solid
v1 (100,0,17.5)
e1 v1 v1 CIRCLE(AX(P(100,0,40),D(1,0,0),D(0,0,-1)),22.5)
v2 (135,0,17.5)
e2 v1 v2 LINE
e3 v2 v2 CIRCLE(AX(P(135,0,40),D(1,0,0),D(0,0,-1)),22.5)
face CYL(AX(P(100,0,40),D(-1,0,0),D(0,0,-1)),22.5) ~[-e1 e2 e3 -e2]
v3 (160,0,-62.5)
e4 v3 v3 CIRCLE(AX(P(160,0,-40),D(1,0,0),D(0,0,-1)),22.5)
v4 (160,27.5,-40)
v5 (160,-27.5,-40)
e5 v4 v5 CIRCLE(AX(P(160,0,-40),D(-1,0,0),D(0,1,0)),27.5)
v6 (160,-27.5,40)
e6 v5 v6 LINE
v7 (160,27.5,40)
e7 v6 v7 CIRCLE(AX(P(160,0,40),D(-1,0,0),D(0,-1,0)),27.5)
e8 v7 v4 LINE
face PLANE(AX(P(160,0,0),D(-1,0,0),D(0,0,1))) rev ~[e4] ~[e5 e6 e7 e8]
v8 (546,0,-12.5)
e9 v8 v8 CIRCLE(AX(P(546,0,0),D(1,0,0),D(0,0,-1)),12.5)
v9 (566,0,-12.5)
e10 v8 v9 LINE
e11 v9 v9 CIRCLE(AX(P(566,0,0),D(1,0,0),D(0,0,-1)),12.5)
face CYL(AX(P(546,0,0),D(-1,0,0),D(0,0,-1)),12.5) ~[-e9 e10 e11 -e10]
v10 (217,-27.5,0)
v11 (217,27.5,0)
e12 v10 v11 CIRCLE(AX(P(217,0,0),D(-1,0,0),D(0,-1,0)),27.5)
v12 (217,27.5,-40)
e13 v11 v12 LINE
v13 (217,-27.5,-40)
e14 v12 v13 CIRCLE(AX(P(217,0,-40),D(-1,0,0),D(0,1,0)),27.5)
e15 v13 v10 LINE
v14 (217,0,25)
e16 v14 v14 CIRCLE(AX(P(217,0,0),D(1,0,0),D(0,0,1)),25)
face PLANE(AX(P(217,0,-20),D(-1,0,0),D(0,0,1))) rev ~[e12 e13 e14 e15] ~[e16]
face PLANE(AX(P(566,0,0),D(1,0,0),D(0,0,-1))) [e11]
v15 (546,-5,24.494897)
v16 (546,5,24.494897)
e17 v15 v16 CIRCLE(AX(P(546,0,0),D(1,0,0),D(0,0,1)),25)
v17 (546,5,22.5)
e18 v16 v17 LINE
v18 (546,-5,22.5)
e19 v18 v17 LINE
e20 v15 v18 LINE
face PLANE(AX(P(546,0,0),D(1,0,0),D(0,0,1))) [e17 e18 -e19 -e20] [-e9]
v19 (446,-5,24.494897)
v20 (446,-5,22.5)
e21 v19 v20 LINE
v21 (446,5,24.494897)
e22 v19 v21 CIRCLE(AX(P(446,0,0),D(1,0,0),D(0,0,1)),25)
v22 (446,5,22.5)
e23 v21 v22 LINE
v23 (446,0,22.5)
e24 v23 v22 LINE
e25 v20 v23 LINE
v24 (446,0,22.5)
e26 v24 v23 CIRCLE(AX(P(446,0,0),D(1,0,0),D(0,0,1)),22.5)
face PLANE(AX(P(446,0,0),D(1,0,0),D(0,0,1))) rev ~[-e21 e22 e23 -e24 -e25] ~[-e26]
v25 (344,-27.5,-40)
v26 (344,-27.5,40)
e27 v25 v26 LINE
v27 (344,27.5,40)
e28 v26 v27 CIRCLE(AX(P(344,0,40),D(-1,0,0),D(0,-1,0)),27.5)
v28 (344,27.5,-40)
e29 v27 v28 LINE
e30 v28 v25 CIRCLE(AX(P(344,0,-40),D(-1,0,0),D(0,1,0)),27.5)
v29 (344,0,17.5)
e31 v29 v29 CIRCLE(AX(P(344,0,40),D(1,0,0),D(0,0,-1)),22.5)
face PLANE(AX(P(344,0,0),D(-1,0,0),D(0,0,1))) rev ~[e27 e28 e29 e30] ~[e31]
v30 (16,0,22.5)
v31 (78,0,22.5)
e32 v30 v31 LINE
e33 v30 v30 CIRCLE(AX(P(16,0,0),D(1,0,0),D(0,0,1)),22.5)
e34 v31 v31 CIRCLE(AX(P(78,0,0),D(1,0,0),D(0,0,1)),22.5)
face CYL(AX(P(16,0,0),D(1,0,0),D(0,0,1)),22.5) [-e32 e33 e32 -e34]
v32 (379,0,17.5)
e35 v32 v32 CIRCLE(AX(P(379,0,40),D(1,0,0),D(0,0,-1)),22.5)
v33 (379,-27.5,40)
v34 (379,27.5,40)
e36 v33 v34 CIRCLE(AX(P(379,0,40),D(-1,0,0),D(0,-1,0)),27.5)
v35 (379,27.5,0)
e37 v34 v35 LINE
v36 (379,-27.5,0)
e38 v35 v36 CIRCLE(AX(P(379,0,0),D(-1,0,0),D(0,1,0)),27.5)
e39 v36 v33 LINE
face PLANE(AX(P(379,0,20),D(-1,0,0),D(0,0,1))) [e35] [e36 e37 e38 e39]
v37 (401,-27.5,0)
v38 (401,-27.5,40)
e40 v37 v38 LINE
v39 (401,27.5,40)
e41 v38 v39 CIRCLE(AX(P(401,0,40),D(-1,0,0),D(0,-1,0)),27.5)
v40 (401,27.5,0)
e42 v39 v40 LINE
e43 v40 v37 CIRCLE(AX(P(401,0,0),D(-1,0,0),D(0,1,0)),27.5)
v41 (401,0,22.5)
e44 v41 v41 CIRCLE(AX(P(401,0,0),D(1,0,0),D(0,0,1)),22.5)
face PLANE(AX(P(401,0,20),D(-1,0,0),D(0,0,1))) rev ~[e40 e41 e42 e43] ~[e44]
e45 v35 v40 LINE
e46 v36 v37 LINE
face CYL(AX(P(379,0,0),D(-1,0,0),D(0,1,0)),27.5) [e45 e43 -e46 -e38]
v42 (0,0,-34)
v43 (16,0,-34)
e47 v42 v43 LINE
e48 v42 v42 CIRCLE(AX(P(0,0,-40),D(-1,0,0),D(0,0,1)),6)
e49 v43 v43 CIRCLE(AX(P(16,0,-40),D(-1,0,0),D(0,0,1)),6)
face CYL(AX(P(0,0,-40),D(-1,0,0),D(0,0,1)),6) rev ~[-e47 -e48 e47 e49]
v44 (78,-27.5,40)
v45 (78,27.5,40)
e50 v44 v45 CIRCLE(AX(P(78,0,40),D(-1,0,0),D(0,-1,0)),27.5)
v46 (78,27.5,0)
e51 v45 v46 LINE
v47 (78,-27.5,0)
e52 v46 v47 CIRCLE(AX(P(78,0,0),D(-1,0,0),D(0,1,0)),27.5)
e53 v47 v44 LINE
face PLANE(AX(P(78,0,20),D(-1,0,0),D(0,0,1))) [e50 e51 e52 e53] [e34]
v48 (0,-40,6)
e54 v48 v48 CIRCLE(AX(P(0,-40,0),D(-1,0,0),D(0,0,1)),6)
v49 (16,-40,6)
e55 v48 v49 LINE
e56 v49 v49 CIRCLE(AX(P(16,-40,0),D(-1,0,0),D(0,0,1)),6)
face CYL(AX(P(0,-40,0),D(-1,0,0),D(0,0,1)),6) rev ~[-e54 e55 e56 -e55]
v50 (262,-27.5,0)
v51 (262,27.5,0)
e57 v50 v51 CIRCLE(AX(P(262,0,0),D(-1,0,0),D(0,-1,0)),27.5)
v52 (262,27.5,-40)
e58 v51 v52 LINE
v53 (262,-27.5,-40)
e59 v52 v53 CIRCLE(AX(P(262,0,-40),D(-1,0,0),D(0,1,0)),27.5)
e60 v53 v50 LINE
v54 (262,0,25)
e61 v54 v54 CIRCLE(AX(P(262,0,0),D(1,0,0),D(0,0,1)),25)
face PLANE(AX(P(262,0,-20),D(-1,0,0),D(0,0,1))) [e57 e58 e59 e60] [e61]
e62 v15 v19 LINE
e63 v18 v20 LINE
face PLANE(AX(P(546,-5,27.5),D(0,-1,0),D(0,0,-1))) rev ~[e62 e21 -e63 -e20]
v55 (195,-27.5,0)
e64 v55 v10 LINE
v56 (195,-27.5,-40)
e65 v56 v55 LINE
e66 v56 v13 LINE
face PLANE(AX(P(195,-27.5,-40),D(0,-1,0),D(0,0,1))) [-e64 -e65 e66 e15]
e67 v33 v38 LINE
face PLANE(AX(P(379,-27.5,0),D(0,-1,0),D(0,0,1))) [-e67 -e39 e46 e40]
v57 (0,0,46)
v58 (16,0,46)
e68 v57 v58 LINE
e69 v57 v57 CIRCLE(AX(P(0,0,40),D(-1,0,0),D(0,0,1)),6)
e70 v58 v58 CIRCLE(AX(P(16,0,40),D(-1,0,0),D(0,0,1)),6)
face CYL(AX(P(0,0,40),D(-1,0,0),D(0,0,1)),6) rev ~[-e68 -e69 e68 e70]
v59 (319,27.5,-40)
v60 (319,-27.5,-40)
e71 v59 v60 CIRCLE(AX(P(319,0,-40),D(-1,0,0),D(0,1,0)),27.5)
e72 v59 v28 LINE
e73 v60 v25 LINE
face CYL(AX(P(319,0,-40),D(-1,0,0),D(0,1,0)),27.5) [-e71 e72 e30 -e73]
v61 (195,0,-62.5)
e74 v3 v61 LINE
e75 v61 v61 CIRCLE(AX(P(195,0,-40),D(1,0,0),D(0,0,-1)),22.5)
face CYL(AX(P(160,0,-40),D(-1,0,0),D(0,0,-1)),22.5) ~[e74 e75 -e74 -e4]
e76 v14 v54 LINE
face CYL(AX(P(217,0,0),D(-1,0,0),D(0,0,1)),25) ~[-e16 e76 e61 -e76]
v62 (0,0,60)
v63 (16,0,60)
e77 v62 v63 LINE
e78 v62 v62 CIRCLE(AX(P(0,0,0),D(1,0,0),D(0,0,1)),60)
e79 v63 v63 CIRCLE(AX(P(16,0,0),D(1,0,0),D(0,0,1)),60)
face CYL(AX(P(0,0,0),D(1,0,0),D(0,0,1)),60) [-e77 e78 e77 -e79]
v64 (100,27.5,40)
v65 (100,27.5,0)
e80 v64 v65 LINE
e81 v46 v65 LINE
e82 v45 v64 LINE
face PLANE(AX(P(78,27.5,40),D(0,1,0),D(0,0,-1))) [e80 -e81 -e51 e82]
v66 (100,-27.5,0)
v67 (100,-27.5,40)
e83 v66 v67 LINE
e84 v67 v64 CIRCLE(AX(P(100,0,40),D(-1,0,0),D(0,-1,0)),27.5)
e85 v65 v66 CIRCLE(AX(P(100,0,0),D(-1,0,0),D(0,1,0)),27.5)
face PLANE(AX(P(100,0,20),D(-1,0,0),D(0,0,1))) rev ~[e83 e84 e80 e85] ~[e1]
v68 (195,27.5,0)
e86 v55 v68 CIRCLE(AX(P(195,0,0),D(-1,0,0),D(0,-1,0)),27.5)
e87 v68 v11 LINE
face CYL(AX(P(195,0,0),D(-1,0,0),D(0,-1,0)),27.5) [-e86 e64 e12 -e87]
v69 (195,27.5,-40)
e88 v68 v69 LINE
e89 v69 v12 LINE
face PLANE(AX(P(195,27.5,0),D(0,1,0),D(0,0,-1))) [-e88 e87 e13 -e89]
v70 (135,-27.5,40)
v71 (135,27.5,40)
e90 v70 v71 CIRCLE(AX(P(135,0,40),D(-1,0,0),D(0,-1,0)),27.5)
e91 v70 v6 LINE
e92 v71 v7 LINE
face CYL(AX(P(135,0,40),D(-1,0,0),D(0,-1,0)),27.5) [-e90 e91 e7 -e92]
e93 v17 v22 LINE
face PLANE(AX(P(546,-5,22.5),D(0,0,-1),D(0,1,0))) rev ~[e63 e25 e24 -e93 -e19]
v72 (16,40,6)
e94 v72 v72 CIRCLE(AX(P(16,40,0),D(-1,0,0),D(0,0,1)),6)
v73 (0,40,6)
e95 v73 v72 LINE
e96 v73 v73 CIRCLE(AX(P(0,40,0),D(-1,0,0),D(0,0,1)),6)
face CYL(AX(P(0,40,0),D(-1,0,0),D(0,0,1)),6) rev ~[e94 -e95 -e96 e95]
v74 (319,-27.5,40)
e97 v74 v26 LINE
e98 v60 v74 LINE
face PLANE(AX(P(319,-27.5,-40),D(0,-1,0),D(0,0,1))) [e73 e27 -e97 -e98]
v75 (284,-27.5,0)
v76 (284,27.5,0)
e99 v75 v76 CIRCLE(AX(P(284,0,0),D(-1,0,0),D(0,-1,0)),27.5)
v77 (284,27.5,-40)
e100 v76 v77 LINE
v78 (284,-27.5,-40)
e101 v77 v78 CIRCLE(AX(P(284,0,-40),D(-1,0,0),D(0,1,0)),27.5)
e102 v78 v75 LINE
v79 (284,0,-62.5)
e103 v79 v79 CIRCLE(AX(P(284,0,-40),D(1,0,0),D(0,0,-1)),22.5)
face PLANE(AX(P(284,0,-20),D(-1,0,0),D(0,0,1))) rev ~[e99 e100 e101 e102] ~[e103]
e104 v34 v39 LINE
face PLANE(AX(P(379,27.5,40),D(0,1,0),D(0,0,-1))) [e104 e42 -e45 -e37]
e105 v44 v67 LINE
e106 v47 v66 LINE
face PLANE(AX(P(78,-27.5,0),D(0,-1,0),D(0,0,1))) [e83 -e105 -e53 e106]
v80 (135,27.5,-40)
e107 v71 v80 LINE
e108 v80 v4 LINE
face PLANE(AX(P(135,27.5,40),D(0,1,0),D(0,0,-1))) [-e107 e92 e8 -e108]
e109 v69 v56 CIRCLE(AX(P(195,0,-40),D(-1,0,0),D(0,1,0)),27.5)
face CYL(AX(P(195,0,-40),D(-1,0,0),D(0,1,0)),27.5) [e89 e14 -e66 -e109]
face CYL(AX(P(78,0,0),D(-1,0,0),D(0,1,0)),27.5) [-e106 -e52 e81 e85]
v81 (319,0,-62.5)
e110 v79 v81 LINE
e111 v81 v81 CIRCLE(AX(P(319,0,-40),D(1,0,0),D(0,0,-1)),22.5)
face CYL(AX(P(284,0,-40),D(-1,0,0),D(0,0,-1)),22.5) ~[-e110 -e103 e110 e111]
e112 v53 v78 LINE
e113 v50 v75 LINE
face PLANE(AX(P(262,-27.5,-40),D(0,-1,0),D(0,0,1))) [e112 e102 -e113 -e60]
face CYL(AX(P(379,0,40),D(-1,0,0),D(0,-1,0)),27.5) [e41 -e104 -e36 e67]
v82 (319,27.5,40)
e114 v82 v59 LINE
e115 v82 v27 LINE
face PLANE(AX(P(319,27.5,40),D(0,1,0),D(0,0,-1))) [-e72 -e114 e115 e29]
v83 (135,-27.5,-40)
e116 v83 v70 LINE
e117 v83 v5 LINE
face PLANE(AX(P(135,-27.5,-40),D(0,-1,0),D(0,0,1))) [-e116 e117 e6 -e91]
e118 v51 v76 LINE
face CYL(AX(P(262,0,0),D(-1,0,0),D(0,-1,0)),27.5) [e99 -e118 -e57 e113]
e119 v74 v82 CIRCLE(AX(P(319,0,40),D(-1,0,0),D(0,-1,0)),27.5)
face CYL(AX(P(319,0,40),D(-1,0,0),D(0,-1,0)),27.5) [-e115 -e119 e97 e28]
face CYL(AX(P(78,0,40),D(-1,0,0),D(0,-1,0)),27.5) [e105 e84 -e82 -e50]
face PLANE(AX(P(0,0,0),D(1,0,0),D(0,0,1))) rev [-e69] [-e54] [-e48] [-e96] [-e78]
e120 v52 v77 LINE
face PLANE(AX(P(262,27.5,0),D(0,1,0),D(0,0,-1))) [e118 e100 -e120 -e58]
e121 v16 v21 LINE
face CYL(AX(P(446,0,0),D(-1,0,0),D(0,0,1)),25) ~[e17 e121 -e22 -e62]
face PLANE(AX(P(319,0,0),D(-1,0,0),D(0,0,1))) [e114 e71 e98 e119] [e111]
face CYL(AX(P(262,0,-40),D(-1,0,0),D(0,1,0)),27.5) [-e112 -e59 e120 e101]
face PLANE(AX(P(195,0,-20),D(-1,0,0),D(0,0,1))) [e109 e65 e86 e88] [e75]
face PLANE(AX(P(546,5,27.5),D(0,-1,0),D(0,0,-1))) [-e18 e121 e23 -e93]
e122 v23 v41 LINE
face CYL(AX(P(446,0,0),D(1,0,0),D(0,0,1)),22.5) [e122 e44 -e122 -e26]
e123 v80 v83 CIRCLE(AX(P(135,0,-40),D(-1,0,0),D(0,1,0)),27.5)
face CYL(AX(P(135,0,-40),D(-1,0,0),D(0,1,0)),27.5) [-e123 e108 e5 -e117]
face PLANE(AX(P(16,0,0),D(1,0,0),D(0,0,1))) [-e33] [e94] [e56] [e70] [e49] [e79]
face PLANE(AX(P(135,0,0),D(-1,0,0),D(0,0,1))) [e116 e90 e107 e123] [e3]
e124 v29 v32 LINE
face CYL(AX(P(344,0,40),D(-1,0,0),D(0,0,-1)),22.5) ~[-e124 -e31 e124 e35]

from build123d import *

# Parameters (mm, degrees)
WEB_1_DEPTH                   = 22
CRANKPIN_1_SKETCH_R           = 22.5
CRANKPIN_1_45_DEPTH           = 35
WEB_2_DEPTH                   = 25
CRANKPIN_2_SKETCH_R           = 22.5
CRANKPIN_2_45_DEPTH           = 35
WEB_3_DEPTH                   = 22
CENTRE_MAIN_JOURNAL_SKETCH_R  = 25
CENTRE_MAIN_JOURNAL_50_DEPTH  = 45
WEB_4_DEPTH                   = 22
CRANKPIN_3_SKETCH_R           = 22.5
CRANKPIN_3_45_DEPTH           = 35
WEB_5_DEPTH                   = 25
CRANKPIN_4_SKETCH_R           = 22.5
CRANKPIN_4_45_DEPTH           = 35
WEB_6_DEPTH                   = 22
FRONT_START                   = 45
FRONT_JOURNAL_SKETCH_R        = 22.5
FRONT_JOURNAL_45_DEPTH        = 45
FRONT_SHAFT_SKETCH_R          = 25
FRONT_SHAFT_50_DEPTH          = 100
NOSE_SKETCH_R                 = 12.5
NOSE_25_DEPTH                 = 20
FLANGE_BOLT_HOLES_SKETCH_R    = 6
FLANGE_BOLT_HOLES_4X_12_DEPTH = 20
KEYWAY_SKETCH_W               = 5
KEYWAY_SKETCH_H               = 10
KEYWAY_10X5_DEPTH             = 110


with BuildPart() as part:
    # Flange Profile Sketch → Flange and Rear Shaft (revolve)
    with BuildSketch(Plane.XY, mode=Mode.PRIVATE) as flange_and_rear_shaft_sk:
        Polygon((0, 0), (0, 60), (16, 60), (16, 22.5), (78, 22.5), (78, 0), align=None)
    revolve(flange_and_rear_shaft_sk.sketch.rotate(Axis((-89.086419753, 0, 0), (1, 0, 0)), 90), axis=Axis((-89.086419753, 0, 0), (1, 0, 0)))

    # Web 1 Sketch → Web 1 (add)
    with BuildSketch(Plane(origin=(78, 0, 0), x_dir=(0, 0, -1), z_dir=(1, 0, 0))):
        with BuildLine():
            Line((0, -27.5), (-40, -27.5))
            ThreePointArc((-40, -27.5), (-67.5, 0), (-40, 27.5))
            Line((-40, 27.5), (0, 27.5))
            ThreePointArc((0, 27.5), (27.5, 0), (0, -27.5))
        make_face()
    extrude(amount=WEB_1_DEPTH)

    # Crankpin 1 Sketch → Crankpin 1 Ø45 (add)
    with BuildSketch(Plane(origin=(100, 0, 0), x_dir=(0, 0, -1), z_dir=(1, 0, 0))):
        with Locations((-40, 0)):
            Circle(CRANKPIN_1_SKETCH_R)
    extrude(amount=CRANKPIN_1_45_DEPTH)

    # Web 2 Sketch → Web 2 (add)
    with BuildSketch(Plane(origin=(135, 0, 0), x_dir=(0, 0, -1), z_dir=(1, 0, 0))):
        with BuildLine():
            Line((-40, 27.5), (40, 27.5))
            ThreePointArc((40, 27.5), (67.5, 0), (40, -27.5))
            Line((40, -27.5), (-40, -27.5))
            ThreePointArc((-40, -27.5), (-67.5, 0), (-40, 27.5))
        make_face()
    extrude(amount=WEB_2_DEPTH)

    # Crankpin 2 Sketch → Crankpin 2 Ø45 (add)
    with BuildSketch(Plane(origin=(160, 0, 0), x_dir=(0, 0, -1), z_dir=(1, 0, 0))):
        with Locations((40, 0)):
            Circle(CRANKPIN_2_SKETCH_R)
    extrude(amount=CRANKPIN_2_45_DEPTH)

    # Web 3 Sketch → Web 3 (add)
    with BuildSketch(Plane(origin=(195, 0, 0), x_dir=(0, 0, -1), z_dir=(1, 0, 0))):
        with BuildLine():
            Line((40, -27.5), (0, -27.5))
            ThreePointArc((0, -27.5), (-27.5, 0), (0, 27.5))
            Line((0, 27.5), (40, 27.5))
            ThreePointArc((40, 27.5), (67.5, 0), (40, -27.5))
        make_face()
    extrude(amount=WEB_3_DEPTH)

    # Centre Main Journal Sketch → Centre Main Journal Ø50 (add)
    with BuildSketch(Plane(origin=(217, 0, 0), x_dir=(0, 0, -1), z_dir=(1, 0, 0))):
        with Locations(Location((0, 0, 0), (0, 0, 180))):
            Circle(CENTRE_MAIN_JOURNAL_SKETCH_R)
    extrude(amount=CENTRE_MAIN_JOURNAL_50_DEPTH)

    # Web 4 Sketch → Web 4 (add)
    with BuildSketch(Plane(origin=(262, 0, 0), x_dir=(0, 0, -1), z_dir=(1, 0, 0))):
        with BuildLine():
            Line((0, 27.5), (40, 27.5))
            ThreePointArc((40, 27.5), (67.5, 0), (40, -27.5))
            Line((40, -27.5), (0, -27.5))
            ThreePointArc((0, -27.5), (-27.5, 0), (0, 27.5))
        make_face()
    extrude(amount=WEB_4_DEPTH)

    # Crankpin 3 Sketch → Crankpin 3 Ø45 (add)
    with BuildSketch(Plane(origin=(284, 0, 0), x_dir=(0, 0, -1), z_dir=(1, 0, 0))):
        with Locations((40, 0)):
            Circle(CRANKPIN_3_SKETCH_R)
    extrude(amount=CRANKPIN_3_45_DEPTH)

    # Web 5 Sketch → Web 5 (add)
    with BuildSketch(Plane(origin=(319, 0, 0), x_dir=(0, 0, -1), z_dir=(1, 0, 0))):
        with BuildLine():
            Line((40, -27.5), (-40, -27.5))
            ThreePointArc((-40, -27.5), (-67.5, 0), (-40, 27.5))
            Line((-40, 27.5), (40, 27.5))
            ThreePointArc((40, 27.5), (67.5, 0), (40, -27.5))
        make_face()
    extrude(amount=WEB_5_DEPTH)

    # Crankpin 4 Sketch → Crankpin 4 Ø45 (add)
    with BuildSketch(Plane(origin=(344, 0, 0), x_dir=(0, 0, -1), z_dir=(1, 0, 0))):
        with Locations((-40, 0)):
            Circle(CRANKPIN_4_SKETCH_R)
    extrude(amount=CRANKPIN_4_45_DEPTH)

    # Web 6 Sketch → Web 6 (add)
    with BuildSketch(Plane(origin=(379, 0, 0), x_dir=(0, 0, -1), z_dir=(1, 0, 0))):
        with BuildLine():
            Line((-40, 27.5), (0, 27.5))
            ThreePointArc((0, 27.5), (27.5, 0), (0, -27.5))
            Line((0, -27.5), (-40, -27.5))
            ThreePointArc((-40, -27.5), (-67.5, 0), (-40, 27.5))
        make_face()
    extrude(amount=WEB_6_DEPTH)

    # Front Journal Sketch → Front Journal Ø45 (add)
    with BuildSketch(Plane(origin=(401, 0, 0), x_dir=(0, 0, -1), z_dir=(1, 0, 0)).offset(FRONT_START)):
        with Locations(Location((0, 0, 0), (0, 0, 180))):
            Circle(FRONT_JOURNAL_SKETCH_R)
    extrude(amount=-FRONT_JOURNAL_45_DEPTH)

    # Front Shaft Sketch → Front Shaft Ø50 (add)
    with BuildSketch(Plane(origin=(446, 0, 0), x_dir=(0, 0, -1), z_dir=(1, 0, 0))):
        with Locations(Location((0, 0, 0), (0, 0, 180))):
            Circle(FRONT_SHAFT_SKETCH_R)
    extrude(amount=FRONT_SHAFT_50_DEPTH)

    # Nose Sketch → Nose Ø25 (add)
    with BuildSketch(Plane(origin=(546, 0, 0), x_dir=(0, 0, -1), z_dir=(1, 0, 0))):
        Circle(NOSE_SKETCH_R)
    extrude(amount=NOSE_25_DEPTH)

    # Flange Bolt Holes Sketch → Flange Bolt Holes 4xØ12 (cut)
    with BuildSketch(Plane.ZY):
        with Locations((0, 40)):
            Circle(FLANGE_BOLT_HOLES_SKETCH_R)
        with Locations((40, 0)):
            Circle(FLANGE_BOLT_HOLES_SKETCH_R)
        with Locations((0, -40)):
            Circle(FLANGE_BOLT_HOLES_SKETCH_R)
        with Locations((-40, 0)):
            Circle(FLANGE_BOLT_HOLES_SKETCH_R)
    extrude(amount=-FLANGE_BOLT_HOLES_4X_12_DEPTH, mode=Mode.SUBTRACT)

    # Keyway Sketch → Keyway 10x5 (cut)
    with BuildSketch(Plane(origin=(546, 0, 0), x_dir=(0, 0, -1), z_dir=(1, 0, 0))):
        with Locations((-25, 0)):
            Rectangle(KEYWAY_SKETCH_W, KEYWAY_SKETCH_H)
    extrude(amount=-KEYWAY_10X5_DEPTH, mode=Mode.SUBTRACT)


solid = part.part
